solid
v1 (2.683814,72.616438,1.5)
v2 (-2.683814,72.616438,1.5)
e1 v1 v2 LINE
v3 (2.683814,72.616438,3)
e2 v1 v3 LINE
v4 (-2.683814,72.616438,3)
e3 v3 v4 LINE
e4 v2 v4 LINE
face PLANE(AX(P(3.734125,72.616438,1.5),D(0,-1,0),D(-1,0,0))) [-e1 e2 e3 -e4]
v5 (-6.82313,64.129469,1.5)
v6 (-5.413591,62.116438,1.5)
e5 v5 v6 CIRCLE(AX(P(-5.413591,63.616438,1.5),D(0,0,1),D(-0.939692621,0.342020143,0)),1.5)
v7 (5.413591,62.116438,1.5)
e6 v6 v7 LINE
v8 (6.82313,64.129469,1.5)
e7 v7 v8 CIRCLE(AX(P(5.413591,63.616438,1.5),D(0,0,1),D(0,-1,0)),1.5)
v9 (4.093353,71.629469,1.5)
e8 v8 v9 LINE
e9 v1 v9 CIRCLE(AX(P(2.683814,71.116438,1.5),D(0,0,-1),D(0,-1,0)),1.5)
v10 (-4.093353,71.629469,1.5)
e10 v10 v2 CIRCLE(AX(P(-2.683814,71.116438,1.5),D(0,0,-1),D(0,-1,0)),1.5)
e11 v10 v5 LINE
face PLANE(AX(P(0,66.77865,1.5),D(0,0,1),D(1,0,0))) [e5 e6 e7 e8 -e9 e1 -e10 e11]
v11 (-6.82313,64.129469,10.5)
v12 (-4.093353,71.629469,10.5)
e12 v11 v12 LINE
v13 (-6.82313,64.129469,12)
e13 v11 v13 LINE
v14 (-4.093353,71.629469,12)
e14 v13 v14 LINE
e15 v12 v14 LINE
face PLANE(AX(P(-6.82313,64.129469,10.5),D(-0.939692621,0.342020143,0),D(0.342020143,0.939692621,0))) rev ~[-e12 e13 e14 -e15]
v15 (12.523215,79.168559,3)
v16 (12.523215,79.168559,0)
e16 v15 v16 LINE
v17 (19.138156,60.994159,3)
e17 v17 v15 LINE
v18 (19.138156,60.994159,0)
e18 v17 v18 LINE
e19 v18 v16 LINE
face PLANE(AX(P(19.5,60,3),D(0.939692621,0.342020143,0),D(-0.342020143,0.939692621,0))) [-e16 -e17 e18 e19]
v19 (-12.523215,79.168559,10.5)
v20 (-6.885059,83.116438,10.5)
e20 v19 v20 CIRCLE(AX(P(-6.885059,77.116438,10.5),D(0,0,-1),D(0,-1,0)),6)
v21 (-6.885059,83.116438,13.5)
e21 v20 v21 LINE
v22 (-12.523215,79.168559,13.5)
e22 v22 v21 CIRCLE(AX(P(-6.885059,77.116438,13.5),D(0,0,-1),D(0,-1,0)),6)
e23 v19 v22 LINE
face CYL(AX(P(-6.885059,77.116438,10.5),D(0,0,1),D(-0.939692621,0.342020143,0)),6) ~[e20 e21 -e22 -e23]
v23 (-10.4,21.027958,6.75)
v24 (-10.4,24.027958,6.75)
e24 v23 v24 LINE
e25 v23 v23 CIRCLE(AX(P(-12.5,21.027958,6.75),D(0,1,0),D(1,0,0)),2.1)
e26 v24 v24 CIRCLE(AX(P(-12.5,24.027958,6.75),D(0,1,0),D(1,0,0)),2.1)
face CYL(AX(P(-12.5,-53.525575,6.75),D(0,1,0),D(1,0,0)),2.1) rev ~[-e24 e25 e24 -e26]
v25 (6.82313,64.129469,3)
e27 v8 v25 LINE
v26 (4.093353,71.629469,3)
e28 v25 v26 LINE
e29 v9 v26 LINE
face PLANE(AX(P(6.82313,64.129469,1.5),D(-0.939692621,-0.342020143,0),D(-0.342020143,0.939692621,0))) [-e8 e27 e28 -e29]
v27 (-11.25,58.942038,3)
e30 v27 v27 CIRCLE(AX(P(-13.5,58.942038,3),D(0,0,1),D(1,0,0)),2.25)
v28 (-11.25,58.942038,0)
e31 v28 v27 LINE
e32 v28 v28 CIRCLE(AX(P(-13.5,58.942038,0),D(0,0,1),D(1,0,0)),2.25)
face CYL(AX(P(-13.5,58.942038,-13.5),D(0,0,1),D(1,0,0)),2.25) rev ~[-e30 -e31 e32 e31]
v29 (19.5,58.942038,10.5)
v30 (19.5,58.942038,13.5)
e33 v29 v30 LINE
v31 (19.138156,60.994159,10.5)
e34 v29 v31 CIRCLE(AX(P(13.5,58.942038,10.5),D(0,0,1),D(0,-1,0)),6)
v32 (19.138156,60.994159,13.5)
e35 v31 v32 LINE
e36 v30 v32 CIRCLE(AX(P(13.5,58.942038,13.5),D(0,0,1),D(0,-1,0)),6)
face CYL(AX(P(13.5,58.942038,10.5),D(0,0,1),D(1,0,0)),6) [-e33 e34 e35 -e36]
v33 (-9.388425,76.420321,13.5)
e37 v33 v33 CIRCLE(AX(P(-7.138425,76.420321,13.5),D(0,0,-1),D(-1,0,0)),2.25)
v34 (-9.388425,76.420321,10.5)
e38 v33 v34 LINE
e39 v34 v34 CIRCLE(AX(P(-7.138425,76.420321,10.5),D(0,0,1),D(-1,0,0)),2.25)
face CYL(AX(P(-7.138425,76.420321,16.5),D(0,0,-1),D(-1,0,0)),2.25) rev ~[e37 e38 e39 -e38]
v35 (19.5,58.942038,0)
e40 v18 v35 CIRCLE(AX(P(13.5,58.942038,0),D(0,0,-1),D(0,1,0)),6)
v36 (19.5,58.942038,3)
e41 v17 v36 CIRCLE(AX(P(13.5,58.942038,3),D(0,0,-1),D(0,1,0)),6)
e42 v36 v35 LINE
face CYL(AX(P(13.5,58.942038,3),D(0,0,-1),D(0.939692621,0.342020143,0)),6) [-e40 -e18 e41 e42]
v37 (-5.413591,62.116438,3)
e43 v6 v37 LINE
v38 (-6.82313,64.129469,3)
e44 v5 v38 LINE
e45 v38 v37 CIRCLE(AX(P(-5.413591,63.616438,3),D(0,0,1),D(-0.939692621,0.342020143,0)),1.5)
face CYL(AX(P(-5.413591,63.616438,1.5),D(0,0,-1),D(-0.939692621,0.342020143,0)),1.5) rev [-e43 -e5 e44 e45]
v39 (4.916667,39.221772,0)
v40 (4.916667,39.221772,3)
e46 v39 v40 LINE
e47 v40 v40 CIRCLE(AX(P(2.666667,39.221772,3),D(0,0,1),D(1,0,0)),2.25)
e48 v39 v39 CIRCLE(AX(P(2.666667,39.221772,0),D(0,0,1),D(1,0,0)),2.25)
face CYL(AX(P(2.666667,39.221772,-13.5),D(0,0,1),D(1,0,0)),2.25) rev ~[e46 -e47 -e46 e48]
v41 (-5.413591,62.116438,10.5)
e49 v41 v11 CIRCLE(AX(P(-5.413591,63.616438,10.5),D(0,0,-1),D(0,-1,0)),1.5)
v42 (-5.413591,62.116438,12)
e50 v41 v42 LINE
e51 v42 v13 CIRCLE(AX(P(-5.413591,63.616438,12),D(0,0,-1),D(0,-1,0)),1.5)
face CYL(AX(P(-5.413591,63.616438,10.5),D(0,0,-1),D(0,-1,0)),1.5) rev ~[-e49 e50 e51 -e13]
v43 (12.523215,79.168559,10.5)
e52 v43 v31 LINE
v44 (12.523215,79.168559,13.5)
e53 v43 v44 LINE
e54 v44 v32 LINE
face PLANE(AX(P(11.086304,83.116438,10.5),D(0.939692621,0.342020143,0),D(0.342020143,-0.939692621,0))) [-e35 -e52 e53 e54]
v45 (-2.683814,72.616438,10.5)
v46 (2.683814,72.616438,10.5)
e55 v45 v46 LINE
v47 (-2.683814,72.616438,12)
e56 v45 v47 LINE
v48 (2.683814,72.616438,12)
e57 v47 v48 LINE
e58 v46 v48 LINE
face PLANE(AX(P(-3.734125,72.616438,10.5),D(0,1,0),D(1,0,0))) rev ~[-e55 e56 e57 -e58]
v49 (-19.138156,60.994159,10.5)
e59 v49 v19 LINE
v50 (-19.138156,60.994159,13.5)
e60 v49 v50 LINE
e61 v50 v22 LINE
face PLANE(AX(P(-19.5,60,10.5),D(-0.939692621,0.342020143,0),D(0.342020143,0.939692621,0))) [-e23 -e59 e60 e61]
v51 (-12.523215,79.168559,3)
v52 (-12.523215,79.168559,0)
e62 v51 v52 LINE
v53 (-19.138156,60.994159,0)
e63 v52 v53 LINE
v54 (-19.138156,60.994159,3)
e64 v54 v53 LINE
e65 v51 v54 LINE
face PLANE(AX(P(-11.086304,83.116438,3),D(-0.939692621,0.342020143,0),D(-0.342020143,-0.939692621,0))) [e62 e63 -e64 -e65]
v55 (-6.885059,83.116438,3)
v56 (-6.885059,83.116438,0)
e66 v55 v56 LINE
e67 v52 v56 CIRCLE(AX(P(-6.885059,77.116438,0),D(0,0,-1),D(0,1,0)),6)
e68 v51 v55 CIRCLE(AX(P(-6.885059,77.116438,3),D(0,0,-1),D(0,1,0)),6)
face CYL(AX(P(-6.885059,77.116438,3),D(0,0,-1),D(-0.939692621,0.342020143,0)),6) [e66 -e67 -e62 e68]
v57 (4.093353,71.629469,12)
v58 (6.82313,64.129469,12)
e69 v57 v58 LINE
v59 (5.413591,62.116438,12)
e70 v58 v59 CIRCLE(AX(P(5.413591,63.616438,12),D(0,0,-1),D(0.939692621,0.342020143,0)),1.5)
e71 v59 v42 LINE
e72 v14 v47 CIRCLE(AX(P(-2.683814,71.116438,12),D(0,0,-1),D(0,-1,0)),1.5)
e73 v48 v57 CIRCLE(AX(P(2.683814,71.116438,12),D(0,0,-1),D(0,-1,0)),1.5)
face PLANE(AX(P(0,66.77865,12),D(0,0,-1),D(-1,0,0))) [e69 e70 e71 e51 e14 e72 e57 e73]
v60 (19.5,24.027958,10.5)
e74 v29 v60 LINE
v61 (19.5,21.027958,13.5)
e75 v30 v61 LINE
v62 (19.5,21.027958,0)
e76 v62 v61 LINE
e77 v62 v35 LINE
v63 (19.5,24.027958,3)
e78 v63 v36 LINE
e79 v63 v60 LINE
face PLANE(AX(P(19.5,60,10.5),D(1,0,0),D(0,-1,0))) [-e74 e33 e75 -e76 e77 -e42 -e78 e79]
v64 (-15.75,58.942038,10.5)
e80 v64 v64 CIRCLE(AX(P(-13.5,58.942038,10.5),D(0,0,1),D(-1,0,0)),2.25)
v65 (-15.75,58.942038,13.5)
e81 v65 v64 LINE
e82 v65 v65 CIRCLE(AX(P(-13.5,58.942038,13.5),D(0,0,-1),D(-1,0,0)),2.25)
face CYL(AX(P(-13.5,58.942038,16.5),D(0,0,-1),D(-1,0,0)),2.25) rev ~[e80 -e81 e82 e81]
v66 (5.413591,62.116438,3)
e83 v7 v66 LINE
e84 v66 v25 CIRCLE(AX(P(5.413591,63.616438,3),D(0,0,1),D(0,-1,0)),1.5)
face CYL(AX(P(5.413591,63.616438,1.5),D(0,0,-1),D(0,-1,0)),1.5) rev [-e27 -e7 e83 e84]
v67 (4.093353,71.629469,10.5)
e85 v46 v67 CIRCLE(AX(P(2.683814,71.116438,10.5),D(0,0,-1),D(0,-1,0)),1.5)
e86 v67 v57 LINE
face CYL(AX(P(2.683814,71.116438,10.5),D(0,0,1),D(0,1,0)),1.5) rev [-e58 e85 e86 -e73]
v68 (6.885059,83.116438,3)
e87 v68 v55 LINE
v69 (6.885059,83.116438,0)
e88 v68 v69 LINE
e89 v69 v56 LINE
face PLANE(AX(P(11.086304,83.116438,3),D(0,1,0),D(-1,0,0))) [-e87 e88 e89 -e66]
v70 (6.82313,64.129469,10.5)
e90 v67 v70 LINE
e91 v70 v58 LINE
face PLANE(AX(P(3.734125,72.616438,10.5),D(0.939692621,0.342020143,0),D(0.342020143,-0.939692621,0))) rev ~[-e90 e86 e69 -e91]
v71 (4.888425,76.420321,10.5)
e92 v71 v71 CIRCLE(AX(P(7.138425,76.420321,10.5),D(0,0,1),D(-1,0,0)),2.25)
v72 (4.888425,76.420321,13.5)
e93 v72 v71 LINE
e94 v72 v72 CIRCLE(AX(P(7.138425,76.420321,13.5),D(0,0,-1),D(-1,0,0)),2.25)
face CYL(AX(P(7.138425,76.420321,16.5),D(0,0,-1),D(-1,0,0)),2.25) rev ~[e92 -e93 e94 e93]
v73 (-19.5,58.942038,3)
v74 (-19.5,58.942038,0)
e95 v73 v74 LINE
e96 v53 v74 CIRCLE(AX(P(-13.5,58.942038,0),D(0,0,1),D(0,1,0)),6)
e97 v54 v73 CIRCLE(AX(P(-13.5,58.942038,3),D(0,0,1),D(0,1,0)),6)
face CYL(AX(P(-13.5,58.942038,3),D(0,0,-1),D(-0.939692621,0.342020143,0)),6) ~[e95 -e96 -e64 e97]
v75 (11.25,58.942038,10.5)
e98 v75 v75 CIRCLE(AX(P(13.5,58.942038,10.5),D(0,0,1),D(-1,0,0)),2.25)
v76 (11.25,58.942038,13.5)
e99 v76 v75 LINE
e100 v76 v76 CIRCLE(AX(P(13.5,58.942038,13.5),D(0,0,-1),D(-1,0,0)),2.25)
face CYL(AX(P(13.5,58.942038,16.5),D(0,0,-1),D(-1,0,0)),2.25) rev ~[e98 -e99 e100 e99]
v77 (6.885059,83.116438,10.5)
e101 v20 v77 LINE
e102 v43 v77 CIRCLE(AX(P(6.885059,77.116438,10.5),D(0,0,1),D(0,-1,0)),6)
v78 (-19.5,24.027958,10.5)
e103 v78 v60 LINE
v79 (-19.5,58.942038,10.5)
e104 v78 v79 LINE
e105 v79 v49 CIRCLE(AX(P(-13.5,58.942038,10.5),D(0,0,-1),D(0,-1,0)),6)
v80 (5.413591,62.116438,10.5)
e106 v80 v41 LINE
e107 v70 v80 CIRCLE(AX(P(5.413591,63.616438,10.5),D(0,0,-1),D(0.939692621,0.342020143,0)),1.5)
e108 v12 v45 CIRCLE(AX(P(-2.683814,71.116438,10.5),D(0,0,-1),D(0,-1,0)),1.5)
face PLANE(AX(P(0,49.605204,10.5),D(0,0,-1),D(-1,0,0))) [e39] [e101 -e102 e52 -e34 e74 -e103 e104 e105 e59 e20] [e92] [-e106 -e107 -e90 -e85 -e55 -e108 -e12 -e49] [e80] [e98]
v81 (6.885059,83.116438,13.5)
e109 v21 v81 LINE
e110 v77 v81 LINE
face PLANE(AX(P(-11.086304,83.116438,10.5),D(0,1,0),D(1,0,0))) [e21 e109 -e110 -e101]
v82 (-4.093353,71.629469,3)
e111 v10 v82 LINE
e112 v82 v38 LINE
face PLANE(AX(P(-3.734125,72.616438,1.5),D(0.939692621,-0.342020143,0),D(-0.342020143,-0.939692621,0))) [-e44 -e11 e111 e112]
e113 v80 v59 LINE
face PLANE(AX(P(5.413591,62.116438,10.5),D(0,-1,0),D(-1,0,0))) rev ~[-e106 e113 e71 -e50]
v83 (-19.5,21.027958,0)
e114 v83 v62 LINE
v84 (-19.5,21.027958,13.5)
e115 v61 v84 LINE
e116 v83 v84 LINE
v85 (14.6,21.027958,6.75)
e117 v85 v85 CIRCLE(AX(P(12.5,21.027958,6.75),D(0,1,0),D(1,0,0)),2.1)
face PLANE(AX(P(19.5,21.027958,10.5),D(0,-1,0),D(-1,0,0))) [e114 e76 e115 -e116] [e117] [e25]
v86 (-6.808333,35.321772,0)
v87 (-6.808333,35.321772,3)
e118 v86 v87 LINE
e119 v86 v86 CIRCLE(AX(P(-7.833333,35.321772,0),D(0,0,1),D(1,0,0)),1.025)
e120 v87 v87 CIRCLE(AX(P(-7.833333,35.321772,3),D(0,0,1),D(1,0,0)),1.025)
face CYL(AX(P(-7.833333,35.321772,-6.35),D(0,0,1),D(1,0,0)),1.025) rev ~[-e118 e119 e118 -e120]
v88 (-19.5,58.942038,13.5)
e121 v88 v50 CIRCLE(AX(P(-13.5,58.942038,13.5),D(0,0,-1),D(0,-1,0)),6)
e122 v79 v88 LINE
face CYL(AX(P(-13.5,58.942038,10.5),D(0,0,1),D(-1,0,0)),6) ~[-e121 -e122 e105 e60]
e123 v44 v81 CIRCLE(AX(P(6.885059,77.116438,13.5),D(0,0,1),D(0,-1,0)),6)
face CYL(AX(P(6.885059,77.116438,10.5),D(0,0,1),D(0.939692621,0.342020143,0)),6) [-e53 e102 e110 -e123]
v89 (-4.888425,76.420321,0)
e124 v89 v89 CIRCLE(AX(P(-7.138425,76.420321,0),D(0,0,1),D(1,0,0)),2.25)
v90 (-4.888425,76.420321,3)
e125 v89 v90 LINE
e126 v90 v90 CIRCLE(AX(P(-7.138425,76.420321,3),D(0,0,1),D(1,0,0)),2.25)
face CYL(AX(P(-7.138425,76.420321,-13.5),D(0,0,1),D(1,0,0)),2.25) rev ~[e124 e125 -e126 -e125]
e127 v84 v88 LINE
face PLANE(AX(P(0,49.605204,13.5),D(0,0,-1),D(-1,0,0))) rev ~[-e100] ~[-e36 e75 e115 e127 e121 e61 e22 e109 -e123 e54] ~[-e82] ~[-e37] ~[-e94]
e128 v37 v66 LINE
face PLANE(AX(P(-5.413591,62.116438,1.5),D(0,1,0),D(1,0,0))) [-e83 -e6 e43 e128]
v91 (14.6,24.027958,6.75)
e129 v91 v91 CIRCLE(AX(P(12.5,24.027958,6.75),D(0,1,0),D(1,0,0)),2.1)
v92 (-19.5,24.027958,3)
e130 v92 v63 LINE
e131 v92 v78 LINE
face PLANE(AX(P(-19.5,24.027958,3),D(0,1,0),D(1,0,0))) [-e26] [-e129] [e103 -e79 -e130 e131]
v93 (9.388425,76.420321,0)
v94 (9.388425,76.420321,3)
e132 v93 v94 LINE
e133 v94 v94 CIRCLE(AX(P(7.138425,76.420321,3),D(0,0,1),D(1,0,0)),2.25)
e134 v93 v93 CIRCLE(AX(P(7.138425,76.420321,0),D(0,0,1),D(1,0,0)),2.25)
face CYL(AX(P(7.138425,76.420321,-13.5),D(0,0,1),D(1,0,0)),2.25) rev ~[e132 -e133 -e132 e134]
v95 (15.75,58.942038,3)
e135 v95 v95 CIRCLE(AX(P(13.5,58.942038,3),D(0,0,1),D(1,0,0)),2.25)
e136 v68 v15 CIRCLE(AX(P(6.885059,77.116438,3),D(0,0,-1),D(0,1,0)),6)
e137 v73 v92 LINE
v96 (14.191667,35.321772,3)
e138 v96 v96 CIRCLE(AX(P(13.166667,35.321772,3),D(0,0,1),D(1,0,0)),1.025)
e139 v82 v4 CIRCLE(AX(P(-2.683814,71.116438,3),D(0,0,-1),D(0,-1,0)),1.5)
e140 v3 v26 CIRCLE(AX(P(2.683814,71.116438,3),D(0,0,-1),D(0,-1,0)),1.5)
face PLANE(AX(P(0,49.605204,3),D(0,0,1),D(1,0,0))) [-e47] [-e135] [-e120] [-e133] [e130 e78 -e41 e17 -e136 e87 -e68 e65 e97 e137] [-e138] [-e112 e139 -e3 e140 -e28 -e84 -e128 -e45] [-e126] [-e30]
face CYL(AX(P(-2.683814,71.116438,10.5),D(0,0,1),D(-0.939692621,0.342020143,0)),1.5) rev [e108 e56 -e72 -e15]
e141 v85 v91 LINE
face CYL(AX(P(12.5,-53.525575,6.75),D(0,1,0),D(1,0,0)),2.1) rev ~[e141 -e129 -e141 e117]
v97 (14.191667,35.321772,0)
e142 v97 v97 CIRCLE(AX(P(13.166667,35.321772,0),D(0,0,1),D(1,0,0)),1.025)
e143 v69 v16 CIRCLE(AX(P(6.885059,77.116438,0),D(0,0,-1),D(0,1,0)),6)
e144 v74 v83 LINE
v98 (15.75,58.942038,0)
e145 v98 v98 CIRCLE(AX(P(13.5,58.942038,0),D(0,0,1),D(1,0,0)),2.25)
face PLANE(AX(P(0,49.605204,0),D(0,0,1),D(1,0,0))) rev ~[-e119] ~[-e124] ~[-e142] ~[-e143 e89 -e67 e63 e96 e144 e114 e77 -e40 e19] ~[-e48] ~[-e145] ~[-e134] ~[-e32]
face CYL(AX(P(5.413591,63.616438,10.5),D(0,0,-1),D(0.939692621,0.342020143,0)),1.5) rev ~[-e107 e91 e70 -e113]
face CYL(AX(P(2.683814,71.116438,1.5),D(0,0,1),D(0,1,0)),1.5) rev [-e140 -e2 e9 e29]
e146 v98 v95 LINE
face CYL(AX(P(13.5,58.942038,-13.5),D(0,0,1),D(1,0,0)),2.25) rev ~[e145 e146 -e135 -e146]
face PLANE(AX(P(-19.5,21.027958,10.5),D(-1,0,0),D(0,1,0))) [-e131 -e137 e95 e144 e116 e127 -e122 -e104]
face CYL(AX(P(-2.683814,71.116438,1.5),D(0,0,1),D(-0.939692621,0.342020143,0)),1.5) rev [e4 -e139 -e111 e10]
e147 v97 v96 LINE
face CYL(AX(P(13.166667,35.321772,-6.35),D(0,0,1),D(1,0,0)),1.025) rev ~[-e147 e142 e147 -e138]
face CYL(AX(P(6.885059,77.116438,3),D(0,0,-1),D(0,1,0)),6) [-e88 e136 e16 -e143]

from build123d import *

# Parameters (mm, degrees)
BOSS_EXTRUDE1_DEPTH            = 10
SKETCH2_W                      = 130
SKETCH2_H                      = 10
BOSS_EXTRUDE2_DEPTH            = 25
BOSS_EXTRUDE3_DEPTH            = 10
CUT_EXTRUDE1_DEPTH             = 5
CUT_EXTRUDE2_START             = -5
CUT_EXTRUDE2_DEPTH             = 5
F_15_0_15_DIAMETER_HOLE1_D     = 15
F_15_0_15_DIAMETER_HOLE1_DEPTH = 10
HOLE1_D                        = 5.1881
HOLE1_DEPTH                    = 10
F_15_0_15_DIAMETER_HOLE2_D     = 15
F_15_0_15_DIAMETER_HOLE2_DEPTH = 45
FILLET1_R                      = 5
FILLET2_R                      = 20
SCALE1_SCALE                   = 0.3
SKETCH14_W                     = 19.347729644
SKETCH14_H                     = 16.426581325
BOSS_EXTRUDE4_DEPTH            = 3
M2_5_TAPPED_HOLE1_D            = 2.05
M2_5_TAPPED_HOLE1_DEPTH        = 6.35
M2_5_TAPPED_HOLE1_TIP          = 0.615882135
M5_TAPPED_HOLE1_D              = 4.2


with BuildPart() as part:
    # Sketch1 → Boss-Extrude1 (new body)
    with BuildSketch(Plane.XY.offset(10)):
        Polygon((-65, 200), (-65, 70.093194396), (65, 70.093194396), (65, 200), (36.954348247, 277.054794904), (-36.954348247, 277.054794904), align=None)
    extrude(amount=-BOSS_EXTRUDE1_DEPTH)

    # Sketch2 → Boss-Extrude2 (add)
    with BuildSketch(Plane.XY.offset(10)):
        with Locations((0, 75.093194396)):
            Rectangle(SKETCH2_W, SKETCH2_H)
    extrude(amount=BOSS_EXTRUDE2_DEPTH)

    # Sketch3 → Boss-Extrude3 (add)
    with BuildSketch(Plane.XY.offset(35)):
        Polygon((-65, 70.093194396), (-65, 200), (-36.954348247, 277.054794904), (36.954348247, 277.054794904), (65, 200), (65, 70.093194396), align=None)
    extrude(amount=BOSS_EXTRUDE3_DEPTH)

    # Sketch4 → Cut-Extrude1 (cut)
    with BuildSketch(Plane(origin=(0, 0, 35), x_dir=(-1, 0, 0), z_dir=(0, 0, -1))):
        with BuildLine():
            Line((-18.045302576, 207.054794904), (18.045302576, 207.054794904))
            ThreePointArc((18.045302576, 207.054794904), (22.141062797, 209.186912723), (22.743765679, 213.764895621))
            Line((22.743765679, 213.764895621), (12.44708441, 242.054794904))
            Line((12.44708441, 242.054794904), (-12.44708441, 242.054794904))
            Line((-12.44708441, 242.054794904), (-22.743765679, 213.764895621))
            ThreePointArc((-22.743765679, 213.764895621), (-22.141062797, 209.186912723), (-18.045302576, 207.054794904))
        make_face()
    extrude(amount=-CUT_EXTRUDE1_DEPTH, mode=Mode.SUBTRACT)

    # Sketch5 → Cut-Extrude2 (cut)
    with BuildSketch(Plane.XY.offset(10).offset(CUT_EXTRUDE2_START)):
        with BuildLine():
            Line((22.743765679, 213.764895621), (12.44708441, 242.054794904))
            Line((12.44708441, 242.054794904), (-12.44708441, 242.054794904))
            Line((-12.44708441, 242.054794904), (-22.743765679, 213.764895621))
            ThreePointArc((-22.743765679, 213.764895621), (-22.141062797, 209.186912723), (-18.045302576, 207.054794904))
            Line((-18.045302576, 207.054794904), (18.045302576, 207.054794904))
            ThreePointArc((18.045302576, 207.054794904), (22.141062797, 209.186912723), (22.743765679, 213.764895621))
        make_face()
    extrude(amount=CUT_EXTRUDE2_DEPTH, mode=Mode.SUBTRACT)

    # Ø15.0 (15) Diameter Hole1
    with Locations(Plane.XY.offset(45)):
        with Locations((8.888888889, 130.739240574), (45, 196.473460386), (-45, 196.473460386), (-23.794751114, 254.734402875), (23.794751114, 254.734402875)):
            Hole(F_15_0_15_DIAMETER_HOLE1_D / 2, depth=F_15_0_15_DIAMETER_HOLE1_DEPTH)

    # Hole1
    with Locations(Plane.XY.offset(45)):
        with Locations((-9.311866244, 122.448733195), (0.59838151, 148.939995706), (27.089644022, 139.029747952), (17.179396267, 112.538485441)):
            Hole(HOLE1_D / 2, depth=HOLE1_DEPTH)

    # Ø15.0 (15) Diameter Hole2
    with Locations(Plane(origin=(0, 0, 0), x_dir=(-1, 0, 0), z_dir=(0, 0, -1))):
        with Locations((-8.888888889, 130.739240574), (-45, 196.473460386), (45, 196.473460386), (23.794751114, 254.734402875), (-23.794751114, 254.734402875)):
            Hole(F_15_0_15_DIAMETER_HOLE2_D / 2, depth=F_15_0_15_DIAMETER_HOLE2_DEPTH)

    # Fillet1
    fillet1_edges = [part.edges().sort_by_distance(p)[0] for p in [
        (12.44708441, 242.054794904, 37.5),
        (-12.44708441, 242.054794904, 37.5),
        (-12.44708441, 242.054794904, 7.5),
        (12.44708441, 242.054794904, 7.5),
    ]]
    fillet(fillet1_edges, radius=FILLET1_R)

    # Fillet2
    fillet2_edges = [part.edges().sort_by_distance(p)[0] for p in [
        (-36.954348247, 277.054794904, 5),
        (36.954348247, 277.054794904, 5),
        (65, 200, 5),
        (-65, 200, 5),
        (65, 200, 40),
        (36.954348247, 277.054794904, 40),
        (-36.954348247, 277.054794904, 40),
        (-65, 200, 40),
    ]]
    fillet(fillet2_edges, radius=FILLET2_R)


with BuildPart() as part_1:
    # Scale1: scaled about (0, 0, 0)
    add(part.part.scale(SCALE1_SCALE))

    # Sketch14 → Boss-Extrude4 (add)
    with BuildSketch(Plane.XY.offset(13.5)):
        with Locations((2.169151432, 38.275577148)):
            Rectangle(SKETCH14_W, SKETCH14_H)
    extrude(amount=-BOSS_EXTRUDE4_DEPTH)

    # M2.5 Tapped Hole1
    with Locations(Plane(origin=(0, 0, 0), x_dir=(-1, 0, 0), z_dir=(0, 0, -1))):
        with Locations((7.833333333, 35.321772172), (-13.166666667, 35.321772172)):
            Hole(M2_5_TAPPED_HOLE1_D / 2, depth=M2_5_TAPPED_HOLE1_DEPTH)
            with Locations((0, 0, -(M2_5_TAPPED_HOLE1_DEPTH + M2_5_TAPPED_HOLE1_TIP / 2))):  # 118° drill point
                Cone(0, M2_5_TAPPED_HOLE1_D / 2, M2_5_TAPPED_HOLE1_TIP, mode=Mode.SUBTRACT)

    # M5 Tapped Hole1 (through all)
    with Locations(Plane(origin=(0, 21.027958319, 0), x_dir=(-1, 0, 0), z_dir=(0, -1, 0))):
        with Locations((12.5, -6.75), (-12.5, -6.75)):
            Hole(M5_TAPPED_HOLE1_D / 2)


solid = part_1.part
